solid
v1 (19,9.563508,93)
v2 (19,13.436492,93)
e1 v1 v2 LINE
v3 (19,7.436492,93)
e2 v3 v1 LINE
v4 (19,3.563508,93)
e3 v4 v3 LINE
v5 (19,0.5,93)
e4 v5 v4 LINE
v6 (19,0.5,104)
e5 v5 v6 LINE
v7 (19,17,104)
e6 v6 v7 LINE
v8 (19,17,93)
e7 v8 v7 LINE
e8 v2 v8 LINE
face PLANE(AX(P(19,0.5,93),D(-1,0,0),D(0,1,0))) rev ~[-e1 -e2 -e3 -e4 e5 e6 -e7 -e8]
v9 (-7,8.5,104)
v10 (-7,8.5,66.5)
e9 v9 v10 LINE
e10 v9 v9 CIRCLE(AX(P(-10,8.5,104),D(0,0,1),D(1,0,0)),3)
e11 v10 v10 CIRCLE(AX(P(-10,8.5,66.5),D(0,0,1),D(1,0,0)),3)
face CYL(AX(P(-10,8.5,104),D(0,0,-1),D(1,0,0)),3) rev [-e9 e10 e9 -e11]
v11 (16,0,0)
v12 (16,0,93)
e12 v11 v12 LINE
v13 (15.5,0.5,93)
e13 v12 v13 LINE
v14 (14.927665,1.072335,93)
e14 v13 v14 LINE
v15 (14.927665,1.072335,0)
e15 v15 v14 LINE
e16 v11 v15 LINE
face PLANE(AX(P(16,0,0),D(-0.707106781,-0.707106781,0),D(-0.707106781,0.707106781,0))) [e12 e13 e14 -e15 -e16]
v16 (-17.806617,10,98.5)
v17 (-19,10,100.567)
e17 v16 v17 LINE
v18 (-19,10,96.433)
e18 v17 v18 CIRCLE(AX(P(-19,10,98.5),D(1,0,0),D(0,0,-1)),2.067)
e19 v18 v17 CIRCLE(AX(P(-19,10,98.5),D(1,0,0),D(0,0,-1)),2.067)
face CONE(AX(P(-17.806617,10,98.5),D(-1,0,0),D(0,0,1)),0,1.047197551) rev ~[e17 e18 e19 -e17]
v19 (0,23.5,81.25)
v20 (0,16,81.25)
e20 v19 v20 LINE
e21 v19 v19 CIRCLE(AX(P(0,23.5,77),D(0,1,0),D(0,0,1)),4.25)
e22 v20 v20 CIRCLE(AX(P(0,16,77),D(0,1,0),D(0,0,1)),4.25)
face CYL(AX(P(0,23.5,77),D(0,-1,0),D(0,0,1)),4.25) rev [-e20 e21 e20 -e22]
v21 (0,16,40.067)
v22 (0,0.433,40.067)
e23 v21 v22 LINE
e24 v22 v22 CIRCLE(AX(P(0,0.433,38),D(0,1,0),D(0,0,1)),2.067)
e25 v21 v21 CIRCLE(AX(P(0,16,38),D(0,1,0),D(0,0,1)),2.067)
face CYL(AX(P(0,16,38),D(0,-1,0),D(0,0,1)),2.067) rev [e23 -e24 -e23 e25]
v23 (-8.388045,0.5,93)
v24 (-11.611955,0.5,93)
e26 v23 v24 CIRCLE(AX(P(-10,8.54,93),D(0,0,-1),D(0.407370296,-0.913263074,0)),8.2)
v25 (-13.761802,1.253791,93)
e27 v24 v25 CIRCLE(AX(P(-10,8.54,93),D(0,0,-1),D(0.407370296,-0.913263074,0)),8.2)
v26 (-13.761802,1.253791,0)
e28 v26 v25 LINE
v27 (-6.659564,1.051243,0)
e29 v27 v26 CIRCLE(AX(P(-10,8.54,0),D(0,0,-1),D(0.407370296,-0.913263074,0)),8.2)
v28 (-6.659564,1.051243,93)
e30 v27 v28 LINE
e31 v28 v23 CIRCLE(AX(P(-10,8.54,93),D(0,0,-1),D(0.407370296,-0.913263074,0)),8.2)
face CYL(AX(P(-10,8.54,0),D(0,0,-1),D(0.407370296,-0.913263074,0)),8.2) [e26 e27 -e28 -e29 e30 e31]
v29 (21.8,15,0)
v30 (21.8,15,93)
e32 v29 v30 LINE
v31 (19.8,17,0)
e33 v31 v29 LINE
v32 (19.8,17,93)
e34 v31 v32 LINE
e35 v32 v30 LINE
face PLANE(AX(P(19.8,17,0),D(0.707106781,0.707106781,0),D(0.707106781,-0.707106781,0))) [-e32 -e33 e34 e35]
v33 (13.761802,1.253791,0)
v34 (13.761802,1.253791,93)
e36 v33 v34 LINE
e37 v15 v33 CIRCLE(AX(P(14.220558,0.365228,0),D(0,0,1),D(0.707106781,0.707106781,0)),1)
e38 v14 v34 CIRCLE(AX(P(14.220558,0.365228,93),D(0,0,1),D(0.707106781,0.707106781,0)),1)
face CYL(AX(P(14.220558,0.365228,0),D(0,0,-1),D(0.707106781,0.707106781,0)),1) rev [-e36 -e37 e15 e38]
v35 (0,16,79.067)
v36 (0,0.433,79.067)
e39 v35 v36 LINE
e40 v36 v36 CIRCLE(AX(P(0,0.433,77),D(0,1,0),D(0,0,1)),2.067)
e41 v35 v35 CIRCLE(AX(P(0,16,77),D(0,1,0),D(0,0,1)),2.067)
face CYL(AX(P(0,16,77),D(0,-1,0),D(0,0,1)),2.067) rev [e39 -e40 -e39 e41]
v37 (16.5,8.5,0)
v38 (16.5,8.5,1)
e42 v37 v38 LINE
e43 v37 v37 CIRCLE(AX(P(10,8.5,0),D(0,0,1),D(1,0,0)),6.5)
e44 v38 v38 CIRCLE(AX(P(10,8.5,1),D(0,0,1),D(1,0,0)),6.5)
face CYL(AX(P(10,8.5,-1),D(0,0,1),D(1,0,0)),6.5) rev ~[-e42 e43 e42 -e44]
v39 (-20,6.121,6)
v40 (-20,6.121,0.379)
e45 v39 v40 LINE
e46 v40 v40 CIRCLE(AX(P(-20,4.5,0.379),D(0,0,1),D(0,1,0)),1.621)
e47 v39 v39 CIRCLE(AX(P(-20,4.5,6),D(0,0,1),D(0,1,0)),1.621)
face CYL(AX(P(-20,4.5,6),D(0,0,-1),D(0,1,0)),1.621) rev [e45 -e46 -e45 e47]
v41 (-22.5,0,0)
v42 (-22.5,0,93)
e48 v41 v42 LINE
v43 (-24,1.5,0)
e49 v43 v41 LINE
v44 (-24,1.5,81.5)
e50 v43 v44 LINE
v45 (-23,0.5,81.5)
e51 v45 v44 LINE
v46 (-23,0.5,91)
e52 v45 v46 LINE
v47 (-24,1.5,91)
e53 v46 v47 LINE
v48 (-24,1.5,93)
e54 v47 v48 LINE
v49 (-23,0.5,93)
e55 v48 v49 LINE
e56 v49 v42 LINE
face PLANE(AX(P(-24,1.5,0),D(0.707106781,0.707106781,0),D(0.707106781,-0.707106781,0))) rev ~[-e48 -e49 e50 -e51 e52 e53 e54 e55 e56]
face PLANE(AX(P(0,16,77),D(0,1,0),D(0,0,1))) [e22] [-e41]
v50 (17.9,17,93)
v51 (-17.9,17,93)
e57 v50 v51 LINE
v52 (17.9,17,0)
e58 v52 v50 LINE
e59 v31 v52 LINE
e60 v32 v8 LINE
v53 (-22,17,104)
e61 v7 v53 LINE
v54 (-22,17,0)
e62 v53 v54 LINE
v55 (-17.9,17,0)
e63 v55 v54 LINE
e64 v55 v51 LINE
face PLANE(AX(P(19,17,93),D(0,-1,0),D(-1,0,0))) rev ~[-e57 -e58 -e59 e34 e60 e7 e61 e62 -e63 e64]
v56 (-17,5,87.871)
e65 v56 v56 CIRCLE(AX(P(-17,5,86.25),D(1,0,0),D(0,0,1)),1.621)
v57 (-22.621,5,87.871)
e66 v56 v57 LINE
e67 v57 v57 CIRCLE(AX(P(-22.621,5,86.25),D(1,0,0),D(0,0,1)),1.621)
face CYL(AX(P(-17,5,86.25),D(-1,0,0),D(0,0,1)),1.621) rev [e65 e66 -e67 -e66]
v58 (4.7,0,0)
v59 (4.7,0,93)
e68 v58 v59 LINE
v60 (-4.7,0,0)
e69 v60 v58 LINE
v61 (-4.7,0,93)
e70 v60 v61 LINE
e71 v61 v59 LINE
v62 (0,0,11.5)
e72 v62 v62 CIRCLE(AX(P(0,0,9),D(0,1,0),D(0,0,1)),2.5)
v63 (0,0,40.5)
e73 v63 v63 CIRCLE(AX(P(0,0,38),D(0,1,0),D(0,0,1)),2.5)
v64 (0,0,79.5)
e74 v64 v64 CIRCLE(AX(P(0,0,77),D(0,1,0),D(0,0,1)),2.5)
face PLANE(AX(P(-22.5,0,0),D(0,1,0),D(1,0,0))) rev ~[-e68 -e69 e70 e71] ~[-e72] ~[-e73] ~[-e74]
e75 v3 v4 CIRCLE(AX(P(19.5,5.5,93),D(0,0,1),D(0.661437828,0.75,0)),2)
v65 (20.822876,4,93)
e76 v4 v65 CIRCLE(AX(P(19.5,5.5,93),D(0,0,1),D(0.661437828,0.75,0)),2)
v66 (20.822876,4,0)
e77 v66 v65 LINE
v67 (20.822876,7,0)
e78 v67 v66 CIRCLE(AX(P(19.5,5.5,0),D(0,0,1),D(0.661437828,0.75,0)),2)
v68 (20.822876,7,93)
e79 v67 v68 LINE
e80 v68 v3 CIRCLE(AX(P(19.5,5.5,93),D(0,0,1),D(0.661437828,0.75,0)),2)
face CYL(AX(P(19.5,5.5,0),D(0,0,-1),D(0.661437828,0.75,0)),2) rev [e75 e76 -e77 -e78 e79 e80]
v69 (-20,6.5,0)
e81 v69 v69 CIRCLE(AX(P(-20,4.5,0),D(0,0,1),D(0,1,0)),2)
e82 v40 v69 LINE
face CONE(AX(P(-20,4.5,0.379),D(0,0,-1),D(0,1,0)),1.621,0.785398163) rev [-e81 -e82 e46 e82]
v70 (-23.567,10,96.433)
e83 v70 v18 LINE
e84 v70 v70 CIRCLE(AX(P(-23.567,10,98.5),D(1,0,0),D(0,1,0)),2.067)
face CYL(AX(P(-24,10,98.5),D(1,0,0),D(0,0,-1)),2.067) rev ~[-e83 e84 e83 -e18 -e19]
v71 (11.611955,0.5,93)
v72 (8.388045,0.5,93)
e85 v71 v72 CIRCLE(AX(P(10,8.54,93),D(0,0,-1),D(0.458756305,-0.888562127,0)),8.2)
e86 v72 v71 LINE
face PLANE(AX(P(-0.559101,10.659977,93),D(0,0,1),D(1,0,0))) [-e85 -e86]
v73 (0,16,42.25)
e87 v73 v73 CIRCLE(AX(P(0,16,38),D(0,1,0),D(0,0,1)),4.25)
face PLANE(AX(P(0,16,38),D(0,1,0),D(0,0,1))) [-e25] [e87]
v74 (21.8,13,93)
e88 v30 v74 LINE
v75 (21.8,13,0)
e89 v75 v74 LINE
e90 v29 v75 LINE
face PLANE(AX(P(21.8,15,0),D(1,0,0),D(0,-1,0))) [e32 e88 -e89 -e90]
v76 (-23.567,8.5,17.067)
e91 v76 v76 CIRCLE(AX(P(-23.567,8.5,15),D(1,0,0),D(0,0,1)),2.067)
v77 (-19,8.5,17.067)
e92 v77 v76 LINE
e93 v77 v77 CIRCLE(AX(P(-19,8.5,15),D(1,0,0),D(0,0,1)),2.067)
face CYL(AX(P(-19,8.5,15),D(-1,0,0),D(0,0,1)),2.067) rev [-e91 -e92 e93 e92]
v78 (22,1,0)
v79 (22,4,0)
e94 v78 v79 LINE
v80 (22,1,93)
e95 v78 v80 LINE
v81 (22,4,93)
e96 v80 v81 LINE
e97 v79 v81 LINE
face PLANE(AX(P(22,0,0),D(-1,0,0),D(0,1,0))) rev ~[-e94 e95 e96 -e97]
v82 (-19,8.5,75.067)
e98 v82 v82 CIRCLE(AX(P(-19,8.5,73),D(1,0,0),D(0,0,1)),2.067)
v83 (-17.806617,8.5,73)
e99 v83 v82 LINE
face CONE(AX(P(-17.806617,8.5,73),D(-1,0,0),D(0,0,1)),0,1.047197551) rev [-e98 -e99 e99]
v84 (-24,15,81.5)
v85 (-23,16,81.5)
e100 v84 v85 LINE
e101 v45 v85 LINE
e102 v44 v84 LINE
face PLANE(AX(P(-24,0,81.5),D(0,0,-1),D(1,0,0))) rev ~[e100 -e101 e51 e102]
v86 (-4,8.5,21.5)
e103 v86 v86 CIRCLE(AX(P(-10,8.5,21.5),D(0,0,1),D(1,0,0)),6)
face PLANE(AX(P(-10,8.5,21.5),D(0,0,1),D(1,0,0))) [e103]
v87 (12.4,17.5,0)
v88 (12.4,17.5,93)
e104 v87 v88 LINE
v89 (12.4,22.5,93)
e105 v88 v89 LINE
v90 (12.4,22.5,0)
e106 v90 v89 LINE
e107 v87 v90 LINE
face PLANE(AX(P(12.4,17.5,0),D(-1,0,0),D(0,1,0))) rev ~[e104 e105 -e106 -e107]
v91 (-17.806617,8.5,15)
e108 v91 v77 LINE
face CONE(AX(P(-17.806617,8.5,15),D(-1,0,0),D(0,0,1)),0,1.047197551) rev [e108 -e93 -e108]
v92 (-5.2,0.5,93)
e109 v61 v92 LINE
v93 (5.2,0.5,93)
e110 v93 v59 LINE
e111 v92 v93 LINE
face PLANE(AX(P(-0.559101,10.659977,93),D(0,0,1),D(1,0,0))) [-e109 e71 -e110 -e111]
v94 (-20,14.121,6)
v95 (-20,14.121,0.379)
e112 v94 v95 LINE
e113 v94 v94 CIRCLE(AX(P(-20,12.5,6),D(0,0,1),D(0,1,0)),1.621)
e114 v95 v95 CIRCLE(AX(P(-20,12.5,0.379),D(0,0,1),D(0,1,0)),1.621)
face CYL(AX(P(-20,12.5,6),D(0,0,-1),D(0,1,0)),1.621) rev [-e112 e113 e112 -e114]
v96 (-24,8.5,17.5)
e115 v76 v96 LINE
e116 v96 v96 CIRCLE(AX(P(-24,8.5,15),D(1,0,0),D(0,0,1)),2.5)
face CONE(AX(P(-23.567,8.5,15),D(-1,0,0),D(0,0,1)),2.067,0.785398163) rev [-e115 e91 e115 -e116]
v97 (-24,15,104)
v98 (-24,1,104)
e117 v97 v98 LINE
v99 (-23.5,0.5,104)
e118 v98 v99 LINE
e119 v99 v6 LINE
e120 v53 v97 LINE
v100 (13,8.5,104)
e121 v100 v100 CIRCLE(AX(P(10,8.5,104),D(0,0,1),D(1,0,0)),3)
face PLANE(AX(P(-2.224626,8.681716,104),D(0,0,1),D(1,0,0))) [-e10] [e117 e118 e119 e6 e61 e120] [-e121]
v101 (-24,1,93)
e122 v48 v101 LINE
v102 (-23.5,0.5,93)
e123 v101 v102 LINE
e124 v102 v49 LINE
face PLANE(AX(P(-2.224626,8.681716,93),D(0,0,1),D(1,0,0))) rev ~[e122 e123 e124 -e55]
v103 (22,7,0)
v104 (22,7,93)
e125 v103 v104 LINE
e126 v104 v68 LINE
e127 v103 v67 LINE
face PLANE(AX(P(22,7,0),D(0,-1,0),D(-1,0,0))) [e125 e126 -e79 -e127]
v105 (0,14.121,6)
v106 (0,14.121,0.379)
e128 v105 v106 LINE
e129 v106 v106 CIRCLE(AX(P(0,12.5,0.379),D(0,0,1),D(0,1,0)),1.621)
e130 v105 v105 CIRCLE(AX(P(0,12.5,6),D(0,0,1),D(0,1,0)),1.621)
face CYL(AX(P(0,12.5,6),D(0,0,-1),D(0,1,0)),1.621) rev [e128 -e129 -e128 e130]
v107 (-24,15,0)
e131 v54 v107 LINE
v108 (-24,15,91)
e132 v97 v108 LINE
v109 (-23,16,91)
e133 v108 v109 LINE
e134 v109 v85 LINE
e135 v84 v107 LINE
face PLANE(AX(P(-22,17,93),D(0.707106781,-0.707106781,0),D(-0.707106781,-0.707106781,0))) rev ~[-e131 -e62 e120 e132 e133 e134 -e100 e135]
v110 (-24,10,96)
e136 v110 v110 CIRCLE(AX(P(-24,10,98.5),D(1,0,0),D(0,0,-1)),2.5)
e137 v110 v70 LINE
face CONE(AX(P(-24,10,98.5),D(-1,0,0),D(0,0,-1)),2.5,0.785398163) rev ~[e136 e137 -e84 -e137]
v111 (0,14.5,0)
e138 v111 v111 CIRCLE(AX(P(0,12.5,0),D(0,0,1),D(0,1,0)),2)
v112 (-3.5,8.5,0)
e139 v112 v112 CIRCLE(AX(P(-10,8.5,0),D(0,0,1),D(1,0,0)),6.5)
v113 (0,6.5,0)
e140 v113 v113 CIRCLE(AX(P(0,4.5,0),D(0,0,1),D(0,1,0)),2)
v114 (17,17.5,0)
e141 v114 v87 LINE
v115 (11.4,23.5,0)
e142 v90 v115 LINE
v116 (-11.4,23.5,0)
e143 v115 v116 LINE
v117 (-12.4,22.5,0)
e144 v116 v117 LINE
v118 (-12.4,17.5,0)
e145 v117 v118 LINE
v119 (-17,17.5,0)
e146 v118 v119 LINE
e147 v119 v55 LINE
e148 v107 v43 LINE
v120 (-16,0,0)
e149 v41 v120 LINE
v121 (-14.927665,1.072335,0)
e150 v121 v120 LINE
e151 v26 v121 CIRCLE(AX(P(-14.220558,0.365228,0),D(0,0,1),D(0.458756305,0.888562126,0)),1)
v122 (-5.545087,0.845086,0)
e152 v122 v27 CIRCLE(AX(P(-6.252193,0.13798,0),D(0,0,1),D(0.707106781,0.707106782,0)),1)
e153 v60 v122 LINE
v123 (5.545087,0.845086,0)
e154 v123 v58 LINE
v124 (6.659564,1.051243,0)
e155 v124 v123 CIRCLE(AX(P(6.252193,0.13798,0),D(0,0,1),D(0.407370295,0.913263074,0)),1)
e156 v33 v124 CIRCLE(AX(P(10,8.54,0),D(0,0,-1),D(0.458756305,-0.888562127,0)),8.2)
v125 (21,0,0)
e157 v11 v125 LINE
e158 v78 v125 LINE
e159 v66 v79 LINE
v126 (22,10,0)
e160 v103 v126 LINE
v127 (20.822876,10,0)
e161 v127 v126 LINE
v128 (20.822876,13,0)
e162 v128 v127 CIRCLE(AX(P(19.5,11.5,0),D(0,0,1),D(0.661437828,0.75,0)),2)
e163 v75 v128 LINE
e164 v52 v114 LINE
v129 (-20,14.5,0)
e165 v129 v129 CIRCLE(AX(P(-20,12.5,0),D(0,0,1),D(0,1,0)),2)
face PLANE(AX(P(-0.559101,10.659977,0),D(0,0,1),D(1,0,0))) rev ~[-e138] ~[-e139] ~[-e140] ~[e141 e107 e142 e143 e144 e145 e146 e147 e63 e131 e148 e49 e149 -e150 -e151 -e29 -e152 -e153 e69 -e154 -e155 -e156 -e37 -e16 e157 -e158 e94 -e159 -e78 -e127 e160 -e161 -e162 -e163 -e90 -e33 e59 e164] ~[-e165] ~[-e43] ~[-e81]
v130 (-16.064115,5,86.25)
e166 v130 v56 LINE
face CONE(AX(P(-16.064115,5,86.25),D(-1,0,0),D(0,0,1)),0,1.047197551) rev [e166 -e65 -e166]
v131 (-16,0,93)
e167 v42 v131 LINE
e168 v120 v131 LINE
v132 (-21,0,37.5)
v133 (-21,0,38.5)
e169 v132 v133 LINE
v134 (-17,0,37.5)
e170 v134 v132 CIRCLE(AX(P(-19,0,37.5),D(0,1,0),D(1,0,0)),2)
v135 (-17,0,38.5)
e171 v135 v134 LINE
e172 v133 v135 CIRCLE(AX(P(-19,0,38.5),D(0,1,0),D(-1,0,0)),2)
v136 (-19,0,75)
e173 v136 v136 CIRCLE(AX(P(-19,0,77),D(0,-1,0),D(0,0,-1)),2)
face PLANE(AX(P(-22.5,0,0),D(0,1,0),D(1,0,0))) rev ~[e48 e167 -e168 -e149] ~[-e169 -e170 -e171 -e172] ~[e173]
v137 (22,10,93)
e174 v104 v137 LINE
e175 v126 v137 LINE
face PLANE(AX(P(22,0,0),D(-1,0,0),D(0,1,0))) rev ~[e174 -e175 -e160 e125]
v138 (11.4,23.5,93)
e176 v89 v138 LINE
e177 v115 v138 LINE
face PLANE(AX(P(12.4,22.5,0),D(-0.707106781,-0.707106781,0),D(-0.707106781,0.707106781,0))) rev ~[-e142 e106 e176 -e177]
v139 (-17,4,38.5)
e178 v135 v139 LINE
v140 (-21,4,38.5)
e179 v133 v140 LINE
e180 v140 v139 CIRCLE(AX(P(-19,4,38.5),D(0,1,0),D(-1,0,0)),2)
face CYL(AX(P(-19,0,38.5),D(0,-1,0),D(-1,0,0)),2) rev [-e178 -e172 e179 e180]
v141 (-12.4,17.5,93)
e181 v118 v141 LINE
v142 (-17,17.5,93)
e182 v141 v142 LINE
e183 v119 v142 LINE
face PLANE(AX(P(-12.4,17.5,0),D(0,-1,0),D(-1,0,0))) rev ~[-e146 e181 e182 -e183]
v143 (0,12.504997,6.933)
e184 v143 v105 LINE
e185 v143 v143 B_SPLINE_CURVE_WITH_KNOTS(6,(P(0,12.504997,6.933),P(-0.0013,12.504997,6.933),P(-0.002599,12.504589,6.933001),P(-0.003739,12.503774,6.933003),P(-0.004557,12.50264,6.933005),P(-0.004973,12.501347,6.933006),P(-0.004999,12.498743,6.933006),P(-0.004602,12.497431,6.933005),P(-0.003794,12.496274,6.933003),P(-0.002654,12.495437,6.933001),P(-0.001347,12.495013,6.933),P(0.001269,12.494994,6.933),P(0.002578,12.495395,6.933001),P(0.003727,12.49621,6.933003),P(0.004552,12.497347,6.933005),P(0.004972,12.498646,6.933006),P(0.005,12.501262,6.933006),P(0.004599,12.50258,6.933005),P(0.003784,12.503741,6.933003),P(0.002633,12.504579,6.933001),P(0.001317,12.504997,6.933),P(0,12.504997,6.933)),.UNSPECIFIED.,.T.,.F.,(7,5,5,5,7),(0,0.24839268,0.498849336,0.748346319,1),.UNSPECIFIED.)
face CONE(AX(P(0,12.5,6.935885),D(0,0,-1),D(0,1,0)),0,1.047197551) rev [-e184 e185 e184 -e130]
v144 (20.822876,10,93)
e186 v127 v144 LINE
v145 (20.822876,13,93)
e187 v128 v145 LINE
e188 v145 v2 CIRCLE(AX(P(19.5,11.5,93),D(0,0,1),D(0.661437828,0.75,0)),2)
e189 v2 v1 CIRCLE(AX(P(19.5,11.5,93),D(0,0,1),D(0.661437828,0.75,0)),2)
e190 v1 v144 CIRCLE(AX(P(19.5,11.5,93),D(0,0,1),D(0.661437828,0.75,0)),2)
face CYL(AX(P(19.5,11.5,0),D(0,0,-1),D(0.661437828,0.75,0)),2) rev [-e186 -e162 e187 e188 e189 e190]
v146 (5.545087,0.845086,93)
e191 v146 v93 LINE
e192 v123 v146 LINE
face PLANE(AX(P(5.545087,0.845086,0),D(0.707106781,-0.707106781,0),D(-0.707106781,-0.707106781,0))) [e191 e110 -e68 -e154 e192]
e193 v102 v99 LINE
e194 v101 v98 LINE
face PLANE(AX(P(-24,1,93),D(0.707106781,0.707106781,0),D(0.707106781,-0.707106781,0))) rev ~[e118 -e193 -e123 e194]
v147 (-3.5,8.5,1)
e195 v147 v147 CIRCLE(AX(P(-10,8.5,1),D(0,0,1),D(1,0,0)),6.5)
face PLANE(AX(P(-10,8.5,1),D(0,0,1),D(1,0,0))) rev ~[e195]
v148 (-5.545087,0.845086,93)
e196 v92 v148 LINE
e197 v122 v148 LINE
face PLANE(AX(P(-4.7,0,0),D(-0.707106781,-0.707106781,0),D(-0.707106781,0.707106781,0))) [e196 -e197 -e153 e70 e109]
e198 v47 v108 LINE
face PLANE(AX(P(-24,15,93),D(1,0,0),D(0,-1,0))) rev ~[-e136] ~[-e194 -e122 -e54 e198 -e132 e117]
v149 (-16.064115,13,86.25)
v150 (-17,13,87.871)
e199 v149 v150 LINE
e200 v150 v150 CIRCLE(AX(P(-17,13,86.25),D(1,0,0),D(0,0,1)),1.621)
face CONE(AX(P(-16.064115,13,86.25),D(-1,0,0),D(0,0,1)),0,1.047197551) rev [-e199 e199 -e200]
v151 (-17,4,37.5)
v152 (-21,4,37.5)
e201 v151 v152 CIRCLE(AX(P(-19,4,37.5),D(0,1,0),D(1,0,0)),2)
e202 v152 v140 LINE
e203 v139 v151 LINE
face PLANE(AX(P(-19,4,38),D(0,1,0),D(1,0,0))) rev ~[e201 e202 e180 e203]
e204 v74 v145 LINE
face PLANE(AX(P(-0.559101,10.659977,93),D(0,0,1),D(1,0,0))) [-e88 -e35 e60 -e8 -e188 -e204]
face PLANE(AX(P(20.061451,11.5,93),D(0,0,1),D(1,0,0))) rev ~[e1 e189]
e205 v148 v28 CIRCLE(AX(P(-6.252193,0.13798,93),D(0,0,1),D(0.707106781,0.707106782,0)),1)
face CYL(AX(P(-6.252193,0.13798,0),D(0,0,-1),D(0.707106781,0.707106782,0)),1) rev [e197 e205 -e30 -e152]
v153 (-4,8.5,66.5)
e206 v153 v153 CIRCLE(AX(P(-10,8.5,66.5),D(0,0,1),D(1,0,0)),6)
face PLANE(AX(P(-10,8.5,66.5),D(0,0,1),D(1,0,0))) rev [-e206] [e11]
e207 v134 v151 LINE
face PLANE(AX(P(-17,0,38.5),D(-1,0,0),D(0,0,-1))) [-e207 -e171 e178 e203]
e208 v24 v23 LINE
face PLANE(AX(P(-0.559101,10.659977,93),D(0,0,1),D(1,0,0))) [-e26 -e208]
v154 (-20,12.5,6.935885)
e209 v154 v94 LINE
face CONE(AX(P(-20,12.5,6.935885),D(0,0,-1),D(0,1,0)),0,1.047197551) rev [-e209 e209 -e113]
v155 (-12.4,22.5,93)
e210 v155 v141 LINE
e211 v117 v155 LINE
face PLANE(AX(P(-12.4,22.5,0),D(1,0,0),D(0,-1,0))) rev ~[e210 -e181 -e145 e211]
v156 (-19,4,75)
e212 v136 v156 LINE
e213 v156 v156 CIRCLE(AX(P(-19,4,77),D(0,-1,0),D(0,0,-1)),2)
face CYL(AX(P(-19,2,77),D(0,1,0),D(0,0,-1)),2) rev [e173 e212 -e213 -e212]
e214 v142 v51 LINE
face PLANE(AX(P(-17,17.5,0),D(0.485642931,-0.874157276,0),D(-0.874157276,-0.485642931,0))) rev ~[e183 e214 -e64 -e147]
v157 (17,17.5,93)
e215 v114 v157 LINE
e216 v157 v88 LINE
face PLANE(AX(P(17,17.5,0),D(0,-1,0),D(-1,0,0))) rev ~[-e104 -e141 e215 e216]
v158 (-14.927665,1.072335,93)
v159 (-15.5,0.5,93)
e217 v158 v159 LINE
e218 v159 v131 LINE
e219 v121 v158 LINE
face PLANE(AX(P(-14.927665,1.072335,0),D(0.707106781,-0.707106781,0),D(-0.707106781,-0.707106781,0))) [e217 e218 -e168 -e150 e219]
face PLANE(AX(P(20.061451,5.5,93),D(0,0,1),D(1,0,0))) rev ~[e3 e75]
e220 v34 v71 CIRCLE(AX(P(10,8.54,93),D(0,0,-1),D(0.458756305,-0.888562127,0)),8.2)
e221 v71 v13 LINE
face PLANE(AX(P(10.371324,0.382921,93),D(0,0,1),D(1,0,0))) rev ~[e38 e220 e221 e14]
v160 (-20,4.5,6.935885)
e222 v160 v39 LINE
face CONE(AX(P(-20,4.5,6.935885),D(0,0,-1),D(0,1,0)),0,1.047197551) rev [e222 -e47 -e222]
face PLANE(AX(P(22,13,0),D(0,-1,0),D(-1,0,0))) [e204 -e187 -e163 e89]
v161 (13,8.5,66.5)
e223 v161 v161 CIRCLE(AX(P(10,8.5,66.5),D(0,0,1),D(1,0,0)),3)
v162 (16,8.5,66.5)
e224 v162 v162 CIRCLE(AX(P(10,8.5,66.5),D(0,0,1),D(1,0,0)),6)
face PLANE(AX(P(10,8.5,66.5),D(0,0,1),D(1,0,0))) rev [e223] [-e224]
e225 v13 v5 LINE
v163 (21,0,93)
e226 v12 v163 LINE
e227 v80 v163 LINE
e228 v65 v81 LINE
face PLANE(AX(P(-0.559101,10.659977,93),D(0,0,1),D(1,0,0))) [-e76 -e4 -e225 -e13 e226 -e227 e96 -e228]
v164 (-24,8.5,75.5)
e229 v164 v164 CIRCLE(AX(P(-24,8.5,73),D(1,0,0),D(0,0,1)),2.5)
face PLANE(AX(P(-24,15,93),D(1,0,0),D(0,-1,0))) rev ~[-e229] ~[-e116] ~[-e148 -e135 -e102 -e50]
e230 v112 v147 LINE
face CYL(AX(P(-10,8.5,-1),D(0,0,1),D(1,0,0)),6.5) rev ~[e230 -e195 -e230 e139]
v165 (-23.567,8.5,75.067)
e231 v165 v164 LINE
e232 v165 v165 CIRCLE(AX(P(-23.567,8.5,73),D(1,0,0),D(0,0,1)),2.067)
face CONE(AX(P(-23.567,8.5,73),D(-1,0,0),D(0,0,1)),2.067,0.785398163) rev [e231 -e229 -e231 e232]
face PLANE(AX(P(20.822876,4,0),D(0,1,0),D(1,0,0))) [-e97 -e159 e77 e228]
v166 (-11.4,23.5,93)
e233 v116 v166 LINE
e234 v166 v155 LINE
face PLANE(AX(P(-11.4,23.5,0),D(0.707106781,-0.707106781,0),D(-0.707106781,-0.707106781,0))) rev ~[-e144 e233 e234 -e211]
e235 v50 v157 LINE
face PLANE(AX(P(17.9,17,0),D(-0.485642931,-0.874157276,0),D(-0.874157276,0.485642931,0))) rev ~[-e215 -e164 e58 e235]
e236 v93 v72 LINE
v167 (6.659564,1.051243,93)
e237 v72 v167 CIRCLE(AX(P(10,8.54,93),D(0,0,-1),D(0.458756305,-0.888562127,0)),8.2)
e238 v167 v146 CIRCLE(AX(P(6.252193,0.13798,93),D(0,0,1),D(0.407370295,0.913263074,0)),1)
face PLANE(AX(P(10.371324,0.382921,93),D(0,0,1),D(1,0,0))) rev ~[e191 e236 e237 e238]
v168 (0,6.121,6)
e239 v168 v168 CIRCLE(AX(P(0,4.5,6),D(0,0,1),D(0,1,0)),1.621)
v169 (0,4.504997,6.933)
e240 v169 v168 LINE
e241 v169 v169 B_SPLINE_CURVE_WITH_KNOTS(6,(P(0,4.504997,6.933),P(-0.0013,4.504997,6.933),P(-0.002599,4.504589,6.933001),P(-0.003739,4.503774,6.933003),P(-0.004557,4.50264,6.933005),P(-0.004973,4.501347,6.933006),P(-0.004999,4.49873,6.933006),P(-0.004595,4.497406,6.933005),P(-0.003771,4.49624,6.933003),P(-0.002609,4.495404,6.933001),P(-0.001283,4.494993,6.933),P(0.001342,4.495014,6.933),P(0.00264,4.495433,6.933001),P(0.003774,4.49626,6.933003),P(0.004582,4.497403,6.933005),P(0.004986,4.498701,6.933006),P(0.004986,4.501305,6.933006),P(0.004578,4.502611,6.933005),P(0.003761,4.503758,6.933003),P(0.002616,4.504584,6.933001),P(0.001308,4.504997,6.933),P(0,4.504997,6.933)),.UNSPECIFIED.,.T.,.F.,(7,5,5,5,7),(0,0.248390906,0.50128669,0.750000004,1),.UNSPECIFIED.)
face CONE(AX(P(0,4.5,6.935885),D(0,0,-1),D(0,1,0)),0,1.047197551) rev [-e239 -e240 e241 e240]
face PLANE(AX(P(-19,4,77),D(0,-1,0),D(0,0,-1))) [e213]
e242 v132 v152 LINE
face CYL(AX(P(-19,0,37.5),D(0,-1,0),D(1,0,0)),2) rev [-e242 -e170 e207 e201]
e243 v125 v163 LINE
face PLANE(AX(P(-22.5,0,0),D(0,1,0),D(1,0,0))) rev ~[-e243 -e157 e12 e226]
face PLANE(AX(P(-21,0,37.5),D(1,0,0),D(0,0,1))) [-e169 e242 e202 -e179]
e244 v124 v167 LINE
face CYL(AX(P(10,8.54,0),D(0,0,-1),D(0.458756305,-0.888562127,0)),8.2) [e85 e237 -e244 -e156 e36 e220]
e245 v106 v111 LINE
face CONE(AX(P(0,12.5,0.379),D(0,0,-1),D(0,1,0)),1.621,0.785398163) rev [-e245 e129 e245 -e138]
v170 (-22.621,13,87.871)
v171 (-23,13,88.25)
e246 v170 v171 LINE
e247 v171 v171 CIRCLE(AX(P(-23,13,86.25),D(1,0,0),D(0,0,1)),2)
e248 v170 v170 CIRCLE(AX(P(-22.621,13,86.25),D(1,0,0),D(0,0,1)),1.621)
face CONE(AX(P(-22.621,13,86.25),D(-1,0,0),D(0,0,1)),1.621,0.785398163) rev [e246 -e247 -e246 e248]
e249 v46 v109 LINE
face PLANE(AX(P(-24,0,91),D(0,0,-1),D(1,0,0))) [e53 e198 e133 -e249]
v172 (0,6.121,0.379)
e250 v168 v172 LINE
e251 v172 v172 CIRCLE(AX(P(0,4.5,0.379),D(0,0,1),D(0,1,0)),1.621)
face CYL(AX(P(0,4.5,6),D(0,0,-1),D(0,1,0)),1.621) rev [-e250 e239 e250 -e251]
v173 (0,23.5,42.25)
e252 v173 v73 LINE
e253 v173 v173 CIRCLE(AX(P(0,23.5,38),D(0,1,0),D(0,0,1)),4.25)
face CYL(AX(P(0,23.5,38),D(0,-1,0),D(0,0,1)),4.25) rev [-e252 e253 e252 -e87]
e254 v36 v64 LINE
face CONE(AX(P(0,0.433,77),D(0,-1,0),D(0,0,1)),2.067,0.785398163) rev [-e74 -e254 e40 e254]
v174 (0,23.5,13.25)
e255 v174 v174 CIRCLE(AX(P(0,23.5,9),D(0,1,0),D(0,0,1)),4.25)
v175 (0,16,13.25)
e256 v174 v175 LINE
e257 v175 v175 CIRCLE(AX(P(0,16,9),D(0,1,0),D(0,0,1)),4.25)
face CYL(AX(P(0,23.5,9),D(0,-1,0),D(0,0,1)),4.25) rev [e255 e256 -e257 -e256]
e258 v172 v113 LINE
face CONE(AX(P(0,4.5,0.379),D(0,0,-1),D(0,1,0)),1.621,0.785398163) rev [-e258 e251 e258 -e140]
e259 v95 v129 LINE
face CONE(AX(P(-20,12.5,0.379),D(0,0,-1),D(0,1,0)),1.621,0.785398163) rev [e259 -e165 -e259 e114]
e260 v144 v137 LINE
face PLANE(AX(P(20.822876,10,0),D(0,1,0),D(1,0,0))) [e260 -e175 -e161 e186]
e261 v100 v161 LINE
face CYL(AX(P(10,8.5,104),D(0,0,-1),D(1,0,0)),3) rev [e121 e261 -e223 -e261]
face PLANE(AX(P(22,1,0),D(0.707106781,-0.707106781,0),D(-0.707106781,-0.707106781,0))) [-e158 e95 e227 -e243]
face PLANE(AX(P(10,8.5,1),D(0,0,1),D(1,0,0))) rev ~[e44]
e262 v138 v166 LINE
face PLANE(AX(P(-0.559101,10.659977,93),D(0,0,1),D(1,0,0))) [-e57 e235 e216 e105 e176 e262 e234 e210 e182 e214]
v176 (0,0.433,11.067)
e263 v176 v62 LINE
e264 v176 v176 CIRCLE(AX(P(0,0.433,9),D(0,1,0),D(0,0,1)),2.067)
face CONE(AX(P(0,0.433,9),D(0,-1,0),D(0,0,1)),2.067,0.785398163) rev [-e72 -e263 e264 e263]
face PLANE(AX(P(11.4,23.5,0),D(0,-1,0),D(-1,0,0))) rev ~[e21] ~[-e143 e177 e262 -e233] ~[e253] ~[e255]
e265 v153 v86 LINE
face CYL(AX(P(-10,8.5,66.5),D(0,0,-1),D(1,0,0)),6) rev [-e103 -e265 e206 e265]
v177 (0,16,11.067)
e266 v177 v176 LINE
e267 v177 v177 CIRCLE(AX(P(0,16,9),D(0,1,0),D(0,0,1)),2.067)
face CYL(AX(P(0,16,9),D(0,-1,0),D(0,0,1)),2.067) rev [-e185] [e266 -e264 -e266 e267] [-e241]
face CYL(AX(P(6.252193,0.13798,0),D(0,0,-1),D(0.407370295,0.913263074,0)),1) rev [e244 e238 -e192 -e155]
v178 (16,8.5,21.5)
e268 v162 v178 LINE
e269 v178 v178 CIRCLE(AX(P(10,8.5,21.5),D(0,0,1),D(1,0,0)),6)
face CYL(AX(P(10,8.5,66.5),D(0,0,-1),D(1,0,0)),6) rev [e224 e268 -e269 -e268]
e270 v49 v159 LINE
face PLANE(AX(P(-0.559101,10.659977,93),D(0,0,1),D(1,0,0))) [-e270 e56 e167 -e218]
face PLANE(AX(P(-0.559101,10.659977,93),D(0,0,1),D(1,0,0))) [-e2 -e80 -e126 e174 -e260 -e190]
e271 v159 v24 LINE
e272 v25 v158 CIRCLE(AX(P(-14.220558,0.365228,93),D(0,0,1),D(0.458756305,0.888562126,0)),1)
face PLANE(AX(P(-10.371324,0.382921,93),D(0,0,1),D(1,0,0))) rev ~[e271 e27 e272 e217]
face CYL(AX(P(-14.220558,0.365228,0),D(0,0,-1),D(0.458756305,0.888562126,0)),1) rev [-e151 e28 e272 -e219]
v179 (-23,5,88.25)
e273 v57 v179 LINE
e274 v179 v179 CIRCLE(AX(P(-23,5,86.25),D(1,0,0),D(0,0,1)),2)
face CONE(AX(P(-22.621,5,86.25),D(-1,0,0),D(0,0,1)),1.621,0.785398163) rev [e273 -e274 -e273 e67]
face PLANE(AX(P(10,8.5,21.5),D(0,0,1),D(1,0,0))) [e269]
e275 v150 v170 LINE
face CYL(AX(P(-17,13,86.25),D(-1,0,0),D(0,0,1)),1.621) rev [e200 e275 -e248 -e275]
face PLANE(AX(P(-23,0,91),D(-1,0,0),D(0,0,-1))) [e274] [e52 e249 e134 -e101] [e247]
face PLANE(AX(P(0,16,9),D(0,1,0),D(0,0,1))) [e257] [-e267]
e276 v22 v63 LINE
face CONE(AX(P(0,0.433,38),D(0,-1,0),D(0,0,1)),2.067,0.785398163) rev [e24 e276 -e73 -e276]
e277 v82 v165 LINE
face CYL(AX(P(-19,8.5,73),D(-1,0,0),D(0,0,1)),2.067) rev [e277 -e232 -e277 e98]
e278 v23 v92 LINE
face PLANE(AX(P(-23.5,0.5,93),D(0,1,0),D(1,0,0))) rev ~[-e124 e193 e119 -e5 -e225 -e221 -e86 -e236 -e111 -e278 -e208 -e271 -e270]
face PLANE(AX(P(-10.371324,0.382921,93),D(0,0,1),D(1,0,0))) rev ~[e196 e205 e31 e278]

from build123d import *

# Parameters (mm, degrees)
EXTRUDE_1_DEPTH             = 93
EXTRUDE_2_DEPTH             = 11
CUT_EXTRUDE_1_DEPTH         = 93
PATTERN_LINEAR_1_COUNT      = 2
PATTERN_LINEAR_1_PITCH      = 6
CUT_EXTRUDE_2_DEPTH         = 93
CUT_EXTRUDE_3_DEPTH         = 93
PATTERN_LINEAR_2_COUNT      = 2
PATTERN_LINEAR_2_PITCH      = 8
PATTERN_LINEAR_2_COUNT_DIR2 = 2
PATTERN_LINEAR_2_PITCH_DIR2 = 20
PATTERN_LINEAR_3_COUNT      = 2
PATTERN_LINEAR_3_PITCH      = 20
CUT_EXTRUDE_4_DEPTH         = 4
PATTERN_LINEAR_4_COUNT      = 2
PATTERN_LINEAR_4_PITCH      = 58
SKETCH_16_W                 = 1
SKETCH_16_H                 = 9.5
CUT_EXTRUDE_5_DEPTH         = 46
SKETCH_21_W                 = 2
SKETCH_21_H                 = 4
CUT_EXTRUDE_6_DEPTH         = 93
PATTERN_LINEAR_5_COUNT      = 2
PATTERN_LINEAR_5_PITCH      = 8
HOLE_WIZARD_4_D             = 13
HOLE_WIZARD_4_DEPTH         = 1
HOLE_WIZARD_5_D             = 13
HOLE_WIZARD_5_DEPTH         = 1
HOLE_WIZARD_6_D             = 4.134
HOLE_WIZARD_6_DEPTH         = 5
HOLE_WIZARD_6_CSINK_D       = 5
HOLE_WIZARD_6_CSINK_ANGLE   = 90
HOLE_WIZARD_6_TIP           = 1.193383006


with BuildPart() as part:
    # 草图1 → 凸台-拉伸1 (new body)
    with BuildSketch(Plane.XY):
        Polygon((-24, 1.5), (-22.5, 0), (22, 0), (22, 17), (17.9, 17), (17, 17.5), (12.4, 17.5), (12.4, 22.5), (11.4, 23.5), (-11.4, 23.5), (-12.4, 22.5), (-12.4, 17.5), (-17, 17.5), (-17.9, 17), (-22, 17), (-24, 15), align=None)
    extrude(amount=EXTRUDE_1_DEPTH)

    # 草图2 → 凸台-拉伸2 (add)
    with BuildSketch(Plane.XY.offset(93)):
        Polygon((-24, 1), (-23.5, 0.5), (19, 0.5), (19, 17), (-22, 17), (-24, 15), align=None)
    extrude(amount=EXTRUDE_2_DEPTH)

    # 草图3 → 切除-拉伸1 (cut)
    with BuildSketch(Plane.XY):
        with BuildLine():
            Line((20.822875656, 4), (22, 4))
            Line((22, 4), (22, 7))
            Line((22, 7), (20.822875656, 7))
            ThreePointArc((20.822875656, 7), (17.5, 5.5), (20.822875656, 4))
        make_face()
    cut_extrude_1 = extrude(amount=CUT_EXTRUDE_1_DEPTH, mode=Mode.SUBTRACT)

    # 阵列(线性)1: 切除-拉伸1 ×2
    with Locations(*[(0, i * PATTERN_LINEAR_1_PITCH, 0) for i in range(1, PATTERN_LINEAR_1_COUNT)]):
        add(cut_extrude_1, mode=Mode.SUBTRACT)

    # 草图5 → 切除-拉伸2 (cut)
    with BuildSketch(Plane.XY):
        with BuildLine():
            Line((4.7, 0), (16, 0))
            Line((16, 0), (14.927664784, 1.072335216))
            ThreePointArc((14.927664784, 1.072335216), (14.37434682, 1.353332174), (13.761801698, 1.253790561))
            ThreePointArc((13.761801698, 1.253790561), (10.233759649, 0.343332602), (6.659563577, 1.051242793))
            ThreePointArc((6.659563577, 1.051242793), (6.070298822, 1.121297778), (5.5450865, 0.8450865))
            Line((5.5450865, 0.8450865), (4.7, 0))
        make_face()
    extrude(amount=CUT_EXTRUDE_2_DEPTH, mode=Mode.SUBTRACT)

    # 草图6 → 切除-拉伸3 (cut)
    with BuildSketch(Plane.XY):
        with BuildLine():
            Line((-16, 0), (-4.7, 0))
            Line((-4.7, 0), (-5.5450865, 0.8450865))
            ThreePointArc((-5.5450865, 0.8450865), (-6.070298822, 1.121297778), (-6.659563577, 1.051242793))
            ThreePointArc((-6.659563577, 1.051242793), (-10.233759649, 0.343332602), (-13.761801698, 1.253790561))
            ThreePointArc((-13.761801698, 1.253790561), (-14.37434682, 1.353332174), (-14.927664784, 1.072335216))
            Line((-14.927664784, 1.072335216), (-16, 0))
        make_face()
    extrude(amount=CUT_EXTRUDE_3_DEPTH, mode=Mode.SUBTRACT)

    # 草图7 → 孔1 (revolve, cut)
    with BuildSketch(Plane(origin=(0, 4.5, 0), x_dir=(0, 1, 0), z_dir=(1, 0, 0))):
        Polygon((0, 0), (0, 6.935884786), (1.621, 6), (1.621, 0.379), (2, 0), align=None)
    hole_wizard_1 = revolve(axis=Axis((0, 4.5, -14.308894879), (0, 0, 1)), mode=Mode.SUBTRACT)

    # 阵列(线性)2: Hole Wizard 1 2 × 2
    with Locations(*[(-j * PATTERN_LINEAR_2_PITCH_DIR2, i * PATTERN_LINEAR_2_PITCH, 0) for i in range(PATTERN_LINEAR_2_COUNT) for j in range(PATTERN_LINEAR_2_COUNT_DIR2) if (i, j) != (0, 0)]):
        add(hole_wizard_1, mode=Mode.SUBTRACT)

    # 草图10 → 切除-旋转1 (revolve, cut)
    with BuildSketch(Plane(origin=(10, 0, 0), x_dir=(0, 0, -1), z_dir=(1, 0, 0)), mode=Mode.PRIVATE) as cut_revolve_1_sk:
        Polygon((-104, 8.5), (-104, 11.5), (-66.5, 11.5), (-66.5, 14.5), (-21.5, 14.5), (-21.5, 8.5), align=None)
    cut_revolve_1 = revolve(cut_revolve_1_sk.sketch.rotate(Axis((10, 8.5, 21.5), (0, 0, 1)), 270), axis=Axis((10, 8.5, 21.5), (0, 0, 1)), mode=Mode.SUBTRACT)

    # 阵列(线性)3: 切除-旋转1 ×2
    with Locations(*[(-i * PATTERN_LINEAR_3_PITCH, 0, 0) for i in range(1, PATTERN_LINEAR_3_COUNT)]):
        add(cut_revolve_1, mode=Mode.SUBTRACT)

    # 草图12 → 切除-拉伸4 (cut)
    with BuildSketch(Plane(origin=(0, 0, 0), x_dir=(1, 0, 0), z_dir=(0, 1, 0))):
        with BuildLine():
            Line((-21, -37.5), (-21, -38.5))
            ThreePointArc((-21, -38.5), (-19, -40.5), (-17, -38.5))
            Line((-17, -38.5), (-17, -37.5))
            ThreePointArc((-17, -37.5), (-19, -35.5), (-21, -37.5))
        make_face()
    extrude(amount=CUT_EXTRUDE_4_DEPTH, mode=Mode.SUBTRACT)

    # 草图13 → 孔2 (revolve, cut)
    with BuildSketch(Plane(origin=(-24, 8.5, 15), x_dir=(0, 0, 1), z_dir=(0, 1, 0))):
        Polygon((0, 0), (0, 6.193383006), (2.067, 5), (2.067, 0.433), (2.5, 0), align=None)
    hole_wizard_2 = revolve(axis=Axis((-38.308894879, 8.5, 15), (1, 0, 0)), mode=Mode.SUBTRACT)

    # 阵列(线性)4: 孔2 ×2
    with Locations(*[(0, 0, i * PATTERN_LINEAR_4_PITCH) for i in range(1, PATTERN_LINEAR_4_COUNT)]):
        add(hole_wizard_2, mode=Mode.SUBTRACT)

    # 草图16 → 切除-拉伸5 (cut)
    with BuildSketch(Plane(origin=(0, 0, 0), x_dir=(1, 0, 0), z_dir=(0, 1, 0))):
        with Locations((-23.5, -86.25)):
            Rectangle(SKETCH_16_W, SKETCH_16_H)
    extrude(amount=CUT_EXTRUDE_5_DEPTH, mode=Mode.SUBTRACT)

    # 草图17 → 切除-旋转2 (revolve, cut)
    with BuildSketch(Plane.XY.offset(9), mode=Mode.PRIVATE) as cut_revolve_2_sk:
        Polygon((0, 23.5), (4.25, 23.5), (4.25, 16), (2.067, 16), (2.067, 0.433), (2.5, 0), (0, 0), align=None)
    revolve(cut_revolve_2_sk.sketch.rotate(Axis((0, 0, 9), (0, 1, 0)), 270), axis=Axis((0, 0, 9), (0, 1, 0)), mode=Mode.SUBTRACT)

    # 草图19 → 切除-旋转3 (revolve, cut)
    with BuildSketch(Plane.XY.offset(77), mode=Mode.PRIVATE) as cut_revolve_3_sk:
        Polygon((0, 23.5), (4.25, 23.5), (4.25, 16), (2.067, 16), (2.067, 0.433), (2.5, 0), (0, 0), align=None)
    revolve(cut_revolve_3_sk.sketch.rotate(Axis((0, 0, 77), (0, 1, 0)), 270), axis=Axis((0, 0, 77), (0, 1, 0)), mode=Mode.SUBTRACT)

    # 草图20 → 切除-旋转4 (revolve, cut)
    with BuildSketch(Plane.XY.offset(38), mode=Mode.PRIVATE) as cut_revolve_4_sk:
        Polygon((0, 23.5), (4.25, 23.5), (4.25, 16), (2.067, 16), (2.067, 0.433), (2.5, 0), (0, 0), align=None)
    revolve(cut_revolve_4_sk.sketch.rotate(Axis((0, 0, 38), (0, 1, 0)), 270), axis=Axis((0, 0, 38), (0, 1, 0)), mode=Mode.SUBTRACT)

    # 草图21 → 切除-旋转5 (revolve, cut)
    with BuildSketch(Plane.XY.offset(77), mode=Mode.PRIVATE) as cut_revolve_5_sk:
        with Locations((-20, 2)):
            Rectangle(SKETCH_21_W, SKETCH_21_H)
    revolve(cut_revolve_5_sk.sketch.rotate(Axis((-19, 4, 77), (0, -1, 0)), 90), axis=Axis((-19, 4, 77), (0, -1, 0)), mode=Mode.SUBTRACT)

    # 草图22 → 切除-拉伸6 (cut)
    with BuildSketch(Plane.XY):
        Polygon((19.8, 17), (21.8, 15), (21.8, 11.5), (22, 11.5), (22, 1), (21, 0), (24, 0), (24, 17), align=None)
    extrude(amount=CUT_EXTRUDE_6_DEPTH, mode=Mode.SUBTRACT)

    # 草图23 → 孔3 (revolve, cut)
    with BuildSketch(Plane(origin=(-23, 5, 86.25), x_dir=(0, 0, 1), z_dir=(0, 1, 0))):
        Polygon((0, 0), (0, 6.935884786), (1.621, 6), (1.621, 0.379), (2, 0), align=None)
    hole_wizard_3 = revolve(axis=Axis((-37.308894879, 5, 86.25), (1, 0, 0)), mode=Mode.SUBTRACT)

    # 阵列(线性)5: 孔3 ×2
    with Locations(*[(0, i * PATTERN_LINEAR_5_PITCH, 0) for i in range(1, PATTERN_LINEAR_5_COUNT)]):
        add(hole_wizard_3, mode=Mode.SUBTRACT)

    # 孔4
    with Locations(Plane(origin=(0, 0, 0), x_dir=(-1, 0, 0), z_dir=(0, 0, -1))):
        with Locations((-10, 8.5)):
            Hole(HOLE_WIZARD_4_D / 2, depth=HOLE_WIZARD_4_DEPTH)

    # 孔5
    with Locations(Plane(origin=(0, 0, 0), x_dir=(-1, 0, 0), z_dir=(0, 0, -1))):
        with Locations((10, 8.5)):
            Hole(HOLE_WIZARD_5_D / 2, depth=HOLE_WIZARD_5_DEPTH)

    # 孔6
    with Locations(Plane.ZY.offset(24)):
        with Locations((98.5, 10)):
            CounterSinkHole(HOLE_WIZARD_6_D / 2, HOLE_WIZARD_6_CSINK_D / 2, depth=HOLE_WIZARD_6_DEPTH, counter_sink_angle=HOLE_WIZARD_6_CSINK_ANGLE)
            with Locations((0, 0, -(HOLE_WIZARD_6_DEPTH + HOLE_WIZARD_6_TIP / 2))):  # 120° drill point
                Cone(0, HOLE_WIZARD_6_D / 2, HOLE_WIZARD_6_TIP, mode=Mode.SUBTRACT)


solid = part.part
